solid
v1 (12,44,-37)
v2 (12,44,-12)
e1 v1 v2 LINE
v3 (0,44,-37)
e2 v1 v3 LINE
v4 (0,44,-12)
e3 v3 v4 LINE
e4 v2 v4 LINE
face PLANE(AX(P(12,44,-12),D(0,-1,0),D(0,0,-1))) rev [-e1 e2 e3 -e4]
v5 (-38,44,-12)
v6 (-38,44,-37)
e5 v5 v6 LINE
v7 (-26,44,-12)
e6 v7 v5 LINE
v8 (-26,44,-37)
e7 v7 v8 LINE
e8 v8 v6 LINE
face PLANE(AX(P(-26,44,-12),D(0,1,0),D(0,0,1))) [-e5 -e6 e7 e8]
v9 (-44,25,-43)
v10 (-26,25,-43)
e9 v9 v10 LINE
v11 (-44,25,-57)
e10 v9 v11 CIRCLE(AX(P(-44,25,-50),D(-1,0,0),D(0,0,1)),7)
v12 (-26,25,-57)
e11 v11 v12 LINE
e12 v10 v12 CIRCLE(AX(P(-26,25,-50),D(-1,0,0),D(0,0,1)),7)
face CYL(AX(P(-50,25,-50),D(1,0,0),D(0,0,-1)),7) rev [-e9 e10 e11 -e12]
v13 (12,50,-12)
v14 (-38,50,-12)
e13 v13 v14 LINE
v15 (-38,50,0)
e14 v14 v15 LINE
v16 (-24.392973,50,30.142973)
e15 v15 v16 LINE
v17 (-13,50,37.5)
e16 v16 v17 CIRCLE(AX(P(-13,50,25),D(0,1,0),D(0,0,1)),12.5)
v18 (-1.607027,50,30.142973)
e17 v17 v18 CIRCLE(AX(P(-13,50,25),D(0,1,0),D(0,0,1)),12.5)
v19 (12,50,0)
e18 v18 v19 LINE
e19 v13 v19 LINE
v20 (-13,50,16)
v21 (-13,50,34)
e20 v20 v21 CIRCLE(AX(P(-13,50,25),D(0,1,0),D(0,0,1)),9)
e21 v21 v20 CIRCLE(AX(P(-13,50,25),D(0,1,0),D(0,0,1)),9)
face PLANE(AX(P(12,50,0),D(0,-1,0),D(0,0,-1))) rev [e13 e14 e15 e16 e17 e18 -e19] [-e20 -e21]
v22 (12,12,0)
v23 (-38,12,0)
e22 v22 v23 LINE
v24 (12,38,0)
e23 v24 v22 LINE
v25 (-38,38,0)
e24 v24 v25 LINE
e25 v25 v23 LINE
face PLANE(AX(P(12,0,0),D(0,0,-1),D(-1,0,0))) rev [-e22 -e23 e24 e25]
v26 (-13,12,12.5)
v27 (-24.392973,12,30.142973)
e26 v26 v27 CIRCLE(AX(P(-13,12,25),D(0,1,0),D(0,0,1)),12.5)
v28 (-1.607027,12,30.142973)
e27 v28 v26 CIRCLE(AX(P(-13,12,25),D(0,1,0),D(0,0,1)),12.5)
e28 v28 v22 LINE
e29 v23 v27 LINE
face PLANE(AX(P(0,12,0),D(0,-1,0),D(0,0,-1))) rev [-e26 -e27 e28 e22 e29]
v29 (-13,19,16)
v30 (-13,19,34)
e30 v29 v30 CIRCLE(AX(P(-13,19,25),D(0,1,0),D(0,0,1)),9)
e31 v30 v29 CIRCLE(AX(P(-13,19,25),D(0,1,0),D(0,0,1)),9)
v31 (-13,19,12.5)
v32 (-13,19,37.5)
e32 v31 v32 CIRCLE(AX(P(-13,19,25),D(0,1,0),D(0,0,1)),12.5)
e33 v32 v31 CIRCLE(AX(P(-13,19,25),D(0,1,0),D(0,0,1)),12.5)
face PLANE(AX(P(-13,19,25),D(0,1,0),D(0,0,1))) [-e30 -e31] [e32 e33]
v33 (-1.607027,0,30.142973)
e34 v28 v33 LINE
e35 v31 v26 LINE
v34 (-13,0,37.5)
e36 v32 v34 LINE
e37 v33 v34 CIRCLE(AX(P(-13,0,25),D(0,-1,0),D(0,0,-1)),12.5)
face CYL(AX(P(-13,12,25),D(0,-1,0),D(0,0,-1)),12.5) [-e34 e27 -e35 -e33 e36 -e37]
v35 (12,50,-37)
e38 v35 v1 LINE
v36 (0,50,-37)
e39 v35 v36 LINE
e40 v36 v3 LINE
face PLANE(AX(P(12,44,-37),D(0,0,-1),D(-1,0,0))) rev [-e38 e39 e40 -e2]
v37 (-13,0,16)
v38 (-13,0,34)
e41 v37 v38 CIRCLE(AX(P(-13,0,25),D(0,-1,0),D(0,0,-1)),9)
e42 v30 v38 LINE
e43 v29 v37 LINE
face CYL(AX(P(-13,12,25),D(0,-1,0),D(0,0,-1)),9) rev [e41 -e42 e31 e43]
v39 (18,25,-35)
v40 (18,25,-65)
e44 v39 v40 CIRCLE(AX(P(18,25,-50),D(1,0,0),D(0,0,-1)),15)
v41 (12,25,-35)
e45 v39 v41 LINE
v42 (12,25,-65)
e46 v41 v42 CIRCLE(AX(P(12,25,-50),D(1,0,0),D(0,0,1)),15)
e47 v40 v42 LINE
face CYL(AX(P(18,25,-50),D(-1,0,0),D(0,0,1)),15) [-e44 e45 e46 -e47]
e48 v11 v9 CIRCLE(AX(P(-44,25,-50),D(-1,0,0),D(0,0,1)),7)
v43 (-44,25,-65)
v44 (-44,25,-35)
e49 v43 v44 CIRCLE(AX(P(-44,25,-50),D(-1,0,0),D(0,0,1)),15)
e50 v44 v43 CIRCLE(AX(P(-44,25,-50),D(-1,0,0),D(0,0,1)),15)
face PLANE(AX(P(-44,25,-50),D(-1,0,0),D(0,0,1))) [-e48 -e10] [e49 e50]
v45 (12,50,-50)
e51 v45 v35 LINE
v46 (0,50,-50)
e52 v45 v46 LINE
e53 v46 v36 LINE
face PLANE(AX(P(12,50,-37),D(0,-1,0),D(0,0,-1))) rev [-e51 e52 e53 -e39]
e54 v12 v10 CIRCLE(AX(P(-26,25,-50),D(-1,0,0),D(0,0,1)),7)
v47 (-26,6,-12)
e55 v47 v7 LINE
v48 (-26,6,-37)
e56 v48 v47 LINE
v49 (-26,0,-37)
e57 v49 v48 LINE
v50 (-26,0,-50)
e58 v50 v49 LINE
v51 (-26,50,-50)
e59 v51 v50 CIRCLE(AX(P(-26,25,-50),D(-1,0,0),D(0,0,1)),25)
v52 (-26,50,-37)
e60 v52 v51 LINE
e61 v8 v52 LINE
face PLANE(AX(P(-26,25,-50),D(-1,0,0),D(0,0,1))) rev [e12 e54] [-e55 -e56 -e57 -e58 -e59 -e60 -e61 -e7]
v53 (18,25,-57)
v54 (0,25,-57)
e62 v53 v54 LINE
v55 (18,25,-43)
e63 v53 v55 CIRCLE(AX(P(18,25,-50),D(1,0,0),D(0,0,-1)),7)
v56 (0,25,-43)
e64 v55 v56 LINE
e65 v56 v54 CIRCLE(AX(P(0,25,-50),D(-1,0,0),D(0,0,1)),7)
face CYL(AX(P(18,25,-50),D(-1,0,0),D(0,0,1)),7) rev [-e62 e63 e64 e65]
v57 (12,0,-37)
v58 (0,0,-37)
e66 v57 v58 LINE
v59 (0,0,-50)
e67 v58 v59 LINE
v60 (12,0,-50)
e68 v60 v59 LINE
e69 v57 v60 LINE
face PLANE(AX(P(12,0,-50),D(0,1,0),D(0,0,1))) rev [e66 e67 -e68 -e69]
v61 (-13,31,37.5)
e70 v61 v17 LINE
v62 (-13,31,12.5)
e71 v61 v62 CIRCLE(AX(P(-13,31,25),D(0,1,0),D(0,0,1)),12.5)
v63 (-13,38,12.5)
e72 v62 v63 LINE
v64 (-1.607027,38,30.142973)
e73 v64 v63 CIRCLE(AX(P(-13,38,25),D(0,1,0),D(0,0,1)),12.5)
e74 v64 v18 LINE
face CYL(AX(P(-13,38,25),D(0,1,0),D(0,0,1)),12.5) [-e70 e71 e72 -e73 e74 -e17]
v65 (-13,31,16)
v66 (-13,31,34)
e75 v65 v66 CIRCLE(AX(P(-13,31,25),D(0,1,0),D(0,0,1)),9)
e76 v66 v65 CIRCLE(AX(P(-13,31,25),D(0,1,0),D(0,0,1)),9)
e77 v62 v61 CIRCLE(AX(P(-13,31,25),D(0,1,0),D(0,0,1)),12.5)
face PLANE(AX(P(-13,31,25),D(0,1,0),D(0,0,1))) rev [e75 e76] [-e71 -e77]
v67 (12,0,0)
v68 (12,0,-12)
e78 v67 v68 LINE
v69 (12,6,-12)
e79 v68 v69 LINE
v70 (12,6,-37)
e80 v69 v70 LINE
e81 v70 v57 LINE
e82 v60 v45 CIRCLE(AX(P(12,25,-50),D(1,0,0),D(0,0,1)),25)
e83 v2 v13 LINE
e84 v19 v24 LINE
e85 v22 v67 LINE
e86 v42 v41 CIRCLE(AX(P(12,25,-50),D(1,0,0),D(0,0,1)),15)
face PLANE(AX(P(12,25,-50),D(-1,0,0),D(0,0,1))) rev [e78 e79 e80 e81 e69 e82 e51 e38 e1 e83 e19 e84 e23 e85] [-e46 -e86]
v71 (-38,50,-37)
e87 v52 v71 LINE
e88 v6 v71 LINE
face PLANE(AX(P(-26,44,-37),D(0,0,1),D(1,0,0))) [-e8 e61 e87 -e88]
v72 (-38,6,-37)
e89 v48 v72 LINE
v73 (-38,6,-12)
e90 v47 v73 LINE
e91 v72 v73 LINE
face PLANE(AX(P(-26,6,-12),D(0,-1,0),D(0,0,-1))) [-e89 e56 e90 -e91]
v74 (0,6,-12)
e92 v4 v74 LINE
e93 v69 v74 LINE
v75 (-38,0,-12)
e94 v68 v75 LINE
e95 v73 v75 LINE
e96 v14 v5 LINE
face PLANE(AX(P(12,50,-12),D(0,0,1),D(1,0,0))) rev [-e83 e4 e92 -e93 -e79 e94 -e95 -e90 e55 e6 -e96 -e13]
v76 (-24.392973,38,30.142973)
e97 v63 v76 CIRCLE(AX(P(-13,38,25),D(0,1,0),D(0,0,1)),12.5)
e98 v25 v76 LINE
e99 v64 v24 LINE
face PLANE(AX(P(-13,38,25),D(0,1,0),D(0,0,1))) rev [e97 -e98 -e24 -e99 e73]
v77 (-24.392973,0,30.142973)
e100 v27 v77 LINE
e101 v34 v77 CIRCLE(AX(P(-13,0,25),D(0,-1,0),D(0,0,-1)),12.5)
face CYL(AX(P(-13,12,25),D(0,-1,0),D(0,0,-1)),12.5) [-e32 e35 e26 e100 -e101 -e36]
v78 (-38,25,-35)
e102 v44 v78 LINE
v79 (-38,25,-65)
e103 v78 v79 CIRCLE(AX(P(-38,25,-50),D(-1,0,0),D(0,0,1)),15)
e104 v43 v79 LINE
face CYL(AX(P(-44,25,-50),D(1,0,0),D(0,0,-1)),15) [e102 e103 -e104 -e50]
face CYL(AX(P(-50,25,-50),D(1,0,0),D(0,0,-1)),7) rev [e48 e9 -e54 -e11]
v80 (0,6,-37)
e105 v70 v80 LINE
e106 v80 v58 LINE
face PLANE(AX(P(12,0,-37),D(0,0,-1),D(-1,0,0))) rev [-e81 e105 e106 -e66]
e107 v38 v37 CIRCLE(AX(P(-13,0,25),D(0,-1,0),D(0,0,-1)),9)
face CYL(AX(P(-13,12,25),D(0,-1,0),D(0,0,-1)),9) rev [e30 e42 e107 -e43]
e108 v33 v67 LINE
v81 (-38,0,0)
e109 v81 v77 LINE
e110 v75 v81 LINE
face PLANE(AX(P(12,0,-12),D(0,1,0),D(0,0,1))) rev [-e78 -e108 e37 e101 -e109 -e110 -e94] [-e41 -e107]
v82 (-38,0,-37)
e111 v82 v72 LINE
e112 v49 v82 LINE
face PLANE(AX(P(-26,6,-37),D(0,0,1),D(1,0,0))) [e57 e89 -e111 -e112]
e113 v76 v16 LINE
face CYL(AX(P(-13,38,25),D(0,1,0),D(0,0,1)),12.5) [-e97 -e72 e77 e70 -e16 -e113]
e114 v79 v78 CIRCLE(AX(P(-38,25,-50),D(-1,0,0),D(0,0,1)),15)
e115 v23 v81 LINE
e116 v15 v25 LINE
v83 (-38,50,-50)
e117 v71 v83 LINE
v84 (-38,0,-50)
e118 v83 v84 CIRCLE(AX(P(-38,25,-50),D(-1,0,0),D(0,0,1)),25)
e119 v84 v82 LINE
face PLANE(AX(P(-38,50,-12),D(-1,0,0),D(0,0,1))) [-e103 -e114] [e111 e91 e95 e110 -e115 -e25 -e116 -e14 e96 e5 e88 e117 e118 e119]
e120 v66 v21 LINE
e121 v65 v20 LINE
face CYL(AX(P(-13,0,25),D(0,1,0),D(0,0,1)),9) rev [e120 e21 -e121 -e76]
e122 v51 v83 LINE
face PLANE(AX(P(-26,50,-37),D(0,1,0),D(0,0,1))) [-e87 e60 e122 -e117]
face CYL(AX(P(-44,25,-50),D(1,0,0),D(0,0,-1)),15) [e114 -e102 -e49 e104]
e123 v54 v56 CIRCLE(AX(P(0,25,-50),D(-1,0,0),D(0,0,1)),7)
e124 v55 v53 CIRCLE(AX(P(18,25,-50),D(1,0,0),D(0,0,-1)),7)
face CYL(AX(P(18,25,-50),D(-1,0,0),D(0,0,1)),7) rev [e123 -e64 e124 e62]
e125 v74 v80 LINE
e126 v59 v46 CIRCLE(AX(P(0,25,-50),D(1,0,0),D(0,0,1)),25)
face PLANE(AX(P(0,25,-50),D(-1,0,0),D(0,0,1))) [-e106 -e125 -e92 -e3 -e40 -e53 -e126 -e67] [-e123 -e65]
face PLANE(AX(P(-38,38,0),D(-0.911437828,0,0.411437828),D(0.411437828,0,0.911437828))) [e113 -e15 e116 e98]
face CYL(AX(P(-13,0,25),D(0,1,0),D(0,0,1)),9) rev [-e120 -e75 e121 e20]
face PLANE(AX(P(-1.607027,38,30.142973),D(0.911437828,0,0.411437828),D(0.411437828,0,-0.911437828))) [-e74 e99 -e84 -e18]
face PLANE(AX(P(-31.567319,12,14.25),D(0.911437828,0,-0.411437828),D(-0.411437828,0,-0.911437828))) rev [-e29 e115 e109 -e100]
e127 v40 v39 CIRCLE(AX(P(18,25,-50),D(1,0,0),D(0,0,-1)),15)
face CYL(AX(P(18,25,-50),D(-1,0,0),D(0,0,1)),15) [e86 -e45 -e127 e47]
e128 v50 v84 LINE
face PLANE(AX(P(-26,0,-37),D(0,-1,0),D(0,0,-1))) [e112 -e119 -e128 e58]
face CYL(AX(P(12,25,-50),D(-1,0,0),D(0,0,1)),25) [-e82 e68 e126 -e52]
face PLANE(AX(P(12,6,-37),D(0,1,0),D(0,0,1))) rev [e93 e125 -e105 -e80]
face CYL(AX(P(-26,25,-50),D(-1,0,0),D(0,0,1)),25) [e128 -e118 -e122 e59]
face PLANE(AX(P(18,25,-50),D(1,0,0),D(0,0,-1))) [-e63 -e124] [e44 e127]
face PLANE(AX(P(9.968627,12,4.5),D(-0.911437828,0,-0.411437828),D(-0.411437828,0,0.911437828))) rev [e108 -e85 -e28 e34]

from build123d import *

# Parameters (mm, degrees)
MAIN_BODY_DEPTH              = 12
UPPER_PLATE_SKETCH_W         = 50
UPPER_PLATE_SKETCH_H         = 50
UPPER_PLATE_DEPTH            = 12
WEB_BLOCK_DEPTH              = 12
PIN_HUB_BOSS_A_SKETCH_R      = 15
PIN_HUB_BOSS_A_SKETCH_R_2    = 7
PIN_HUB_BOSS_A_30_DEPTH      = 6
PIN_START                    = -62
PIN_BORE_SKETCH_R            = 7
PIN_BORE_14_DEPTH            = 62
PIN_START_2                  = 6
PIN_HUB_BOSS_B_SKETCH_R      = 15
PIN_HUB_BOSS_B_SKETCH_R_2    = 7
PIN_HUB_BOSS_B_30_DEPTH      = 6
FORK_LUG_DEPTH               = 12
FORK_HUB_SKETCH_R            = 12.5
FORK_HUB_25_DEPTH            = 19
FORK_BORE_SKETCH_R           = 9
FORK_BORE_18_DEPTH           = 101.304536288
FORK_START                   = -12
FORK_FILLER_BLOCK_SKETCH_R   = 12.5
FORK_FILLER_BLOCK_SKETCH_R_2 = 9
FORK_FILLER_BLOCK_DEPTH      = 12
FORK_START_2                 = 7
FORK_SPACER_RING_SKETCH_R    = 12.5
FORK_SPACER_RING_SKETCH_R_2  = 9
FORK_SPACER_RING_25_DEPTH    = 7


with BuildPart() as part:
    # Main Body Side Profile Sketch → Main Body (new body)
    with BuildSketch(Plane(origin=(0, 0, 0), x_dir=(0, 0, -1), z_dir=(1, 0, 0))):
        with BuildLine():
            Line((0, 0), (0, 50))
            Line((0, 50), (12, 50))
            Line((12, 50), (12, 44))
            Line((12, 44), (37, 44))
            Line((37, 44), (37, 50))
            Line((37, 50), (50, 50))
            ThreePointArc((50, 50), (75, 25), (50, 0))
            Line((50, 0), (37, 0))
            Line((37, 0), (37, 6))
            Line((37, 6), (12, 6))
            Line((12, 6), (12, 0))
            Line((12, 0), (0, 0))
        make_face()
    extrude(amount=MAIN_BODY_DEPTH)

    # Upper Plate Sketch → Upper Plate (add)
    with BuildSketch(Plane.XY):
        with Locations((-13, 25)):
            Rectangle(UPPER_PLATE_SKETCH_W, UPPER_PLATE_SKETCH_H)
    extrude(amount=-UPPER_PLATE_DEPTH)

    # Web Block Sketch → Web Block (add)
    with BuildSketch(Plane.ZY.offset(38)):
        with BuildLine():
            Line((-12, 44), (-37, 44))
            Line((-37, 44), (-37, 50))
            Line((-37, 50), (-50, 50))
            ThreePointArc((-50, 50), (-75, 25), (-50, 0))
            Line((-50, 0), (-37, 0))
            Line((-37, 0), (-37, 6))
            Line((-37, 6), (-12, 6))
            Line((-12, 6), (-12, 44))
        make_face()
    extrude(amount=-WEB_BLOCK_DEPTH)

    # Pin Hub Boss A Sketch → Pin Hub Boss A Ø30 (add)
    with BuildSketch(Plane(origin=(12, 0, 0), x_dir=(0, 0, -1), z_dir=(1, 0, 0))):
        with Locations(Location((50, 25, 0), (0, 0, 180))):
            Circle(PIN_HUB_BOSS_A_SKETCH_R)
        with Locations((50, 25)):
            Circle(PIN_HUB_BOSS_A_SKETCH_R_2, mode=Mode.SUBTRACT)
    extrude(amount=PIN_HUB_BOSS_A_30_DEPTH)

    # Pin Bore Sketch → Pin Bore Ø14 (cut)
    with BuildSketch(Plane(origin=(12, 0, 0), x_dir=(0, 0, -1), z_dir=(1, 0, 0)).offset(PIN_START)):
        with Locations(Location((50, 25, 0), (0, 0, 180))):
            Circle(PIN_BORE_SKETCH_R)
    extrude(amount=PIN_BORE_14_DEPTH, mode=Mode.SUBTRACT)

    # Pin Hub Boss B Sketch → Pin Hub Boss B Ø30 (add)
    with BuildSketch(Plane.ZY.offset(38).offset(PIN_START_2)):
        with Locations((-50, 25)):
            Circle(PIN_HUB_BOSS_B_SKETCH_R)
        with Locations((-50, 25)):
            Circle(PIN_HUB_BOSS_B_SKETCH_R_2, mode=Mode.SUBTRACT)
    extrude(amount=-PIN_HUB_BOSS_B_30_DEPTH)

    # Fork Lug Sketch → Fork Lug (add)
    with BuildSketch(Plane(origin=(0, 50, 0), x_dir=(1, 0, 0), z_dir=(0, 1, 0))):
        with BuildLine():
            Line((-38, 0), (-24.392972847, -30.142972847))
            ThreePointArc((-24.392972847, -30.142972847), (-13, -37.5), (-1.607027153, -30.142972847))
            Line((-1.607027153, -30.142972847), (12, 0))
            Line((12, 0), (-38, 0))
        make_face()
    extrude(amount=-FORK_LUG_DEPTH)

    # Fork Hub Sketch → Fork Hub Ø25 (add)
    with BuildSketch(Plane(origin=(0, 50, 0), x_dir=(1, 0, 0), z_dir=(0, 1, 0))):
        with Locations(Location((-13, -25, 0), (0, 0, 270))):
            Circle(FORK_HUB_SKETCH_R)
    extrude(amount=-FORK_HUB_25_DEPTH)

    # Fork Bore Sketch → Fork Bore Ø18 (cut, through all)
    with BuildSketch(Plane(origin=(0, 50, 0), x_dir=(1, 0, 0), z_dir=(0, 1, 0))):
        with Locations(Location((-13, -25, 0), (0, 0, 270))):
            Circle(FORK_BORE_SKETCH_R)
    extrude(amount=-FORK_BORE_18_DEPTH, mode=Mode.SUBTRACT)

    # Fork Filler Block Sketch → Fork Filler Block (add)
    # profile 1 of 2: a face of its own
    with BuildSketch(Plane.XZ.offset(FORK_START)):
        with BuildLine():
            Line((-24.392972847, 30.142972847), (-38, 0))
            Line((-38, 0), (12, 0))
            Line((12, 0), (-1.607027153, 30.142972847))
            ThreePointArc((-1.607027153, 30.142972847), (-0.779890332, 27.630383946), (-0.5, 25))
            ThreePointArc((-0.5, 25), (-15.630383946, 12.779890332), (-24.392972847, 30.142972847))
        make_face()
    # profile 2 of 2: a face of its own
    with BuildSketch(Plane.XZ.offset(FORK_START)):
        with Locations(Location((-13, 25, 0), (0, 0, 90))):
            Circle(FORK_FILLER_BLOCK_SKETCH_R)
        with Locations(Location((-13, 25, 0), (0, 0, 90))):
            Circle(FORK_FILLER_BLOCK_SKETCH_R_2, mode=Mode.SUBTRACT)
    extrude(amount=FORK_FILLER_BLOCK_DEPTH)

    # Fork Spacer Ring Sketch → Fork Spacer Ring Ø25 (add)
    with BuildSketch(Plane(origin=(0, 12, 0), x_dir=(1, 0, 0), z_dir=(0, 1, 0)).offset(FORK_START_2)):
        with Locations(Location((-13, -25, 0), (0, 0, 270))):
            Circle(FORK_SPACER_RING_SKETCH_R)
        with Locations(Location((-13, -25, 0), (0, 0, 270))):
            Circle(FORK_SPACER_RING_SKETCH_R_2, mode=Mode.SUBTRACT)
    extrude(amount=-FORK_SPACER_RING_25_DEPTH)


solid = part.part
